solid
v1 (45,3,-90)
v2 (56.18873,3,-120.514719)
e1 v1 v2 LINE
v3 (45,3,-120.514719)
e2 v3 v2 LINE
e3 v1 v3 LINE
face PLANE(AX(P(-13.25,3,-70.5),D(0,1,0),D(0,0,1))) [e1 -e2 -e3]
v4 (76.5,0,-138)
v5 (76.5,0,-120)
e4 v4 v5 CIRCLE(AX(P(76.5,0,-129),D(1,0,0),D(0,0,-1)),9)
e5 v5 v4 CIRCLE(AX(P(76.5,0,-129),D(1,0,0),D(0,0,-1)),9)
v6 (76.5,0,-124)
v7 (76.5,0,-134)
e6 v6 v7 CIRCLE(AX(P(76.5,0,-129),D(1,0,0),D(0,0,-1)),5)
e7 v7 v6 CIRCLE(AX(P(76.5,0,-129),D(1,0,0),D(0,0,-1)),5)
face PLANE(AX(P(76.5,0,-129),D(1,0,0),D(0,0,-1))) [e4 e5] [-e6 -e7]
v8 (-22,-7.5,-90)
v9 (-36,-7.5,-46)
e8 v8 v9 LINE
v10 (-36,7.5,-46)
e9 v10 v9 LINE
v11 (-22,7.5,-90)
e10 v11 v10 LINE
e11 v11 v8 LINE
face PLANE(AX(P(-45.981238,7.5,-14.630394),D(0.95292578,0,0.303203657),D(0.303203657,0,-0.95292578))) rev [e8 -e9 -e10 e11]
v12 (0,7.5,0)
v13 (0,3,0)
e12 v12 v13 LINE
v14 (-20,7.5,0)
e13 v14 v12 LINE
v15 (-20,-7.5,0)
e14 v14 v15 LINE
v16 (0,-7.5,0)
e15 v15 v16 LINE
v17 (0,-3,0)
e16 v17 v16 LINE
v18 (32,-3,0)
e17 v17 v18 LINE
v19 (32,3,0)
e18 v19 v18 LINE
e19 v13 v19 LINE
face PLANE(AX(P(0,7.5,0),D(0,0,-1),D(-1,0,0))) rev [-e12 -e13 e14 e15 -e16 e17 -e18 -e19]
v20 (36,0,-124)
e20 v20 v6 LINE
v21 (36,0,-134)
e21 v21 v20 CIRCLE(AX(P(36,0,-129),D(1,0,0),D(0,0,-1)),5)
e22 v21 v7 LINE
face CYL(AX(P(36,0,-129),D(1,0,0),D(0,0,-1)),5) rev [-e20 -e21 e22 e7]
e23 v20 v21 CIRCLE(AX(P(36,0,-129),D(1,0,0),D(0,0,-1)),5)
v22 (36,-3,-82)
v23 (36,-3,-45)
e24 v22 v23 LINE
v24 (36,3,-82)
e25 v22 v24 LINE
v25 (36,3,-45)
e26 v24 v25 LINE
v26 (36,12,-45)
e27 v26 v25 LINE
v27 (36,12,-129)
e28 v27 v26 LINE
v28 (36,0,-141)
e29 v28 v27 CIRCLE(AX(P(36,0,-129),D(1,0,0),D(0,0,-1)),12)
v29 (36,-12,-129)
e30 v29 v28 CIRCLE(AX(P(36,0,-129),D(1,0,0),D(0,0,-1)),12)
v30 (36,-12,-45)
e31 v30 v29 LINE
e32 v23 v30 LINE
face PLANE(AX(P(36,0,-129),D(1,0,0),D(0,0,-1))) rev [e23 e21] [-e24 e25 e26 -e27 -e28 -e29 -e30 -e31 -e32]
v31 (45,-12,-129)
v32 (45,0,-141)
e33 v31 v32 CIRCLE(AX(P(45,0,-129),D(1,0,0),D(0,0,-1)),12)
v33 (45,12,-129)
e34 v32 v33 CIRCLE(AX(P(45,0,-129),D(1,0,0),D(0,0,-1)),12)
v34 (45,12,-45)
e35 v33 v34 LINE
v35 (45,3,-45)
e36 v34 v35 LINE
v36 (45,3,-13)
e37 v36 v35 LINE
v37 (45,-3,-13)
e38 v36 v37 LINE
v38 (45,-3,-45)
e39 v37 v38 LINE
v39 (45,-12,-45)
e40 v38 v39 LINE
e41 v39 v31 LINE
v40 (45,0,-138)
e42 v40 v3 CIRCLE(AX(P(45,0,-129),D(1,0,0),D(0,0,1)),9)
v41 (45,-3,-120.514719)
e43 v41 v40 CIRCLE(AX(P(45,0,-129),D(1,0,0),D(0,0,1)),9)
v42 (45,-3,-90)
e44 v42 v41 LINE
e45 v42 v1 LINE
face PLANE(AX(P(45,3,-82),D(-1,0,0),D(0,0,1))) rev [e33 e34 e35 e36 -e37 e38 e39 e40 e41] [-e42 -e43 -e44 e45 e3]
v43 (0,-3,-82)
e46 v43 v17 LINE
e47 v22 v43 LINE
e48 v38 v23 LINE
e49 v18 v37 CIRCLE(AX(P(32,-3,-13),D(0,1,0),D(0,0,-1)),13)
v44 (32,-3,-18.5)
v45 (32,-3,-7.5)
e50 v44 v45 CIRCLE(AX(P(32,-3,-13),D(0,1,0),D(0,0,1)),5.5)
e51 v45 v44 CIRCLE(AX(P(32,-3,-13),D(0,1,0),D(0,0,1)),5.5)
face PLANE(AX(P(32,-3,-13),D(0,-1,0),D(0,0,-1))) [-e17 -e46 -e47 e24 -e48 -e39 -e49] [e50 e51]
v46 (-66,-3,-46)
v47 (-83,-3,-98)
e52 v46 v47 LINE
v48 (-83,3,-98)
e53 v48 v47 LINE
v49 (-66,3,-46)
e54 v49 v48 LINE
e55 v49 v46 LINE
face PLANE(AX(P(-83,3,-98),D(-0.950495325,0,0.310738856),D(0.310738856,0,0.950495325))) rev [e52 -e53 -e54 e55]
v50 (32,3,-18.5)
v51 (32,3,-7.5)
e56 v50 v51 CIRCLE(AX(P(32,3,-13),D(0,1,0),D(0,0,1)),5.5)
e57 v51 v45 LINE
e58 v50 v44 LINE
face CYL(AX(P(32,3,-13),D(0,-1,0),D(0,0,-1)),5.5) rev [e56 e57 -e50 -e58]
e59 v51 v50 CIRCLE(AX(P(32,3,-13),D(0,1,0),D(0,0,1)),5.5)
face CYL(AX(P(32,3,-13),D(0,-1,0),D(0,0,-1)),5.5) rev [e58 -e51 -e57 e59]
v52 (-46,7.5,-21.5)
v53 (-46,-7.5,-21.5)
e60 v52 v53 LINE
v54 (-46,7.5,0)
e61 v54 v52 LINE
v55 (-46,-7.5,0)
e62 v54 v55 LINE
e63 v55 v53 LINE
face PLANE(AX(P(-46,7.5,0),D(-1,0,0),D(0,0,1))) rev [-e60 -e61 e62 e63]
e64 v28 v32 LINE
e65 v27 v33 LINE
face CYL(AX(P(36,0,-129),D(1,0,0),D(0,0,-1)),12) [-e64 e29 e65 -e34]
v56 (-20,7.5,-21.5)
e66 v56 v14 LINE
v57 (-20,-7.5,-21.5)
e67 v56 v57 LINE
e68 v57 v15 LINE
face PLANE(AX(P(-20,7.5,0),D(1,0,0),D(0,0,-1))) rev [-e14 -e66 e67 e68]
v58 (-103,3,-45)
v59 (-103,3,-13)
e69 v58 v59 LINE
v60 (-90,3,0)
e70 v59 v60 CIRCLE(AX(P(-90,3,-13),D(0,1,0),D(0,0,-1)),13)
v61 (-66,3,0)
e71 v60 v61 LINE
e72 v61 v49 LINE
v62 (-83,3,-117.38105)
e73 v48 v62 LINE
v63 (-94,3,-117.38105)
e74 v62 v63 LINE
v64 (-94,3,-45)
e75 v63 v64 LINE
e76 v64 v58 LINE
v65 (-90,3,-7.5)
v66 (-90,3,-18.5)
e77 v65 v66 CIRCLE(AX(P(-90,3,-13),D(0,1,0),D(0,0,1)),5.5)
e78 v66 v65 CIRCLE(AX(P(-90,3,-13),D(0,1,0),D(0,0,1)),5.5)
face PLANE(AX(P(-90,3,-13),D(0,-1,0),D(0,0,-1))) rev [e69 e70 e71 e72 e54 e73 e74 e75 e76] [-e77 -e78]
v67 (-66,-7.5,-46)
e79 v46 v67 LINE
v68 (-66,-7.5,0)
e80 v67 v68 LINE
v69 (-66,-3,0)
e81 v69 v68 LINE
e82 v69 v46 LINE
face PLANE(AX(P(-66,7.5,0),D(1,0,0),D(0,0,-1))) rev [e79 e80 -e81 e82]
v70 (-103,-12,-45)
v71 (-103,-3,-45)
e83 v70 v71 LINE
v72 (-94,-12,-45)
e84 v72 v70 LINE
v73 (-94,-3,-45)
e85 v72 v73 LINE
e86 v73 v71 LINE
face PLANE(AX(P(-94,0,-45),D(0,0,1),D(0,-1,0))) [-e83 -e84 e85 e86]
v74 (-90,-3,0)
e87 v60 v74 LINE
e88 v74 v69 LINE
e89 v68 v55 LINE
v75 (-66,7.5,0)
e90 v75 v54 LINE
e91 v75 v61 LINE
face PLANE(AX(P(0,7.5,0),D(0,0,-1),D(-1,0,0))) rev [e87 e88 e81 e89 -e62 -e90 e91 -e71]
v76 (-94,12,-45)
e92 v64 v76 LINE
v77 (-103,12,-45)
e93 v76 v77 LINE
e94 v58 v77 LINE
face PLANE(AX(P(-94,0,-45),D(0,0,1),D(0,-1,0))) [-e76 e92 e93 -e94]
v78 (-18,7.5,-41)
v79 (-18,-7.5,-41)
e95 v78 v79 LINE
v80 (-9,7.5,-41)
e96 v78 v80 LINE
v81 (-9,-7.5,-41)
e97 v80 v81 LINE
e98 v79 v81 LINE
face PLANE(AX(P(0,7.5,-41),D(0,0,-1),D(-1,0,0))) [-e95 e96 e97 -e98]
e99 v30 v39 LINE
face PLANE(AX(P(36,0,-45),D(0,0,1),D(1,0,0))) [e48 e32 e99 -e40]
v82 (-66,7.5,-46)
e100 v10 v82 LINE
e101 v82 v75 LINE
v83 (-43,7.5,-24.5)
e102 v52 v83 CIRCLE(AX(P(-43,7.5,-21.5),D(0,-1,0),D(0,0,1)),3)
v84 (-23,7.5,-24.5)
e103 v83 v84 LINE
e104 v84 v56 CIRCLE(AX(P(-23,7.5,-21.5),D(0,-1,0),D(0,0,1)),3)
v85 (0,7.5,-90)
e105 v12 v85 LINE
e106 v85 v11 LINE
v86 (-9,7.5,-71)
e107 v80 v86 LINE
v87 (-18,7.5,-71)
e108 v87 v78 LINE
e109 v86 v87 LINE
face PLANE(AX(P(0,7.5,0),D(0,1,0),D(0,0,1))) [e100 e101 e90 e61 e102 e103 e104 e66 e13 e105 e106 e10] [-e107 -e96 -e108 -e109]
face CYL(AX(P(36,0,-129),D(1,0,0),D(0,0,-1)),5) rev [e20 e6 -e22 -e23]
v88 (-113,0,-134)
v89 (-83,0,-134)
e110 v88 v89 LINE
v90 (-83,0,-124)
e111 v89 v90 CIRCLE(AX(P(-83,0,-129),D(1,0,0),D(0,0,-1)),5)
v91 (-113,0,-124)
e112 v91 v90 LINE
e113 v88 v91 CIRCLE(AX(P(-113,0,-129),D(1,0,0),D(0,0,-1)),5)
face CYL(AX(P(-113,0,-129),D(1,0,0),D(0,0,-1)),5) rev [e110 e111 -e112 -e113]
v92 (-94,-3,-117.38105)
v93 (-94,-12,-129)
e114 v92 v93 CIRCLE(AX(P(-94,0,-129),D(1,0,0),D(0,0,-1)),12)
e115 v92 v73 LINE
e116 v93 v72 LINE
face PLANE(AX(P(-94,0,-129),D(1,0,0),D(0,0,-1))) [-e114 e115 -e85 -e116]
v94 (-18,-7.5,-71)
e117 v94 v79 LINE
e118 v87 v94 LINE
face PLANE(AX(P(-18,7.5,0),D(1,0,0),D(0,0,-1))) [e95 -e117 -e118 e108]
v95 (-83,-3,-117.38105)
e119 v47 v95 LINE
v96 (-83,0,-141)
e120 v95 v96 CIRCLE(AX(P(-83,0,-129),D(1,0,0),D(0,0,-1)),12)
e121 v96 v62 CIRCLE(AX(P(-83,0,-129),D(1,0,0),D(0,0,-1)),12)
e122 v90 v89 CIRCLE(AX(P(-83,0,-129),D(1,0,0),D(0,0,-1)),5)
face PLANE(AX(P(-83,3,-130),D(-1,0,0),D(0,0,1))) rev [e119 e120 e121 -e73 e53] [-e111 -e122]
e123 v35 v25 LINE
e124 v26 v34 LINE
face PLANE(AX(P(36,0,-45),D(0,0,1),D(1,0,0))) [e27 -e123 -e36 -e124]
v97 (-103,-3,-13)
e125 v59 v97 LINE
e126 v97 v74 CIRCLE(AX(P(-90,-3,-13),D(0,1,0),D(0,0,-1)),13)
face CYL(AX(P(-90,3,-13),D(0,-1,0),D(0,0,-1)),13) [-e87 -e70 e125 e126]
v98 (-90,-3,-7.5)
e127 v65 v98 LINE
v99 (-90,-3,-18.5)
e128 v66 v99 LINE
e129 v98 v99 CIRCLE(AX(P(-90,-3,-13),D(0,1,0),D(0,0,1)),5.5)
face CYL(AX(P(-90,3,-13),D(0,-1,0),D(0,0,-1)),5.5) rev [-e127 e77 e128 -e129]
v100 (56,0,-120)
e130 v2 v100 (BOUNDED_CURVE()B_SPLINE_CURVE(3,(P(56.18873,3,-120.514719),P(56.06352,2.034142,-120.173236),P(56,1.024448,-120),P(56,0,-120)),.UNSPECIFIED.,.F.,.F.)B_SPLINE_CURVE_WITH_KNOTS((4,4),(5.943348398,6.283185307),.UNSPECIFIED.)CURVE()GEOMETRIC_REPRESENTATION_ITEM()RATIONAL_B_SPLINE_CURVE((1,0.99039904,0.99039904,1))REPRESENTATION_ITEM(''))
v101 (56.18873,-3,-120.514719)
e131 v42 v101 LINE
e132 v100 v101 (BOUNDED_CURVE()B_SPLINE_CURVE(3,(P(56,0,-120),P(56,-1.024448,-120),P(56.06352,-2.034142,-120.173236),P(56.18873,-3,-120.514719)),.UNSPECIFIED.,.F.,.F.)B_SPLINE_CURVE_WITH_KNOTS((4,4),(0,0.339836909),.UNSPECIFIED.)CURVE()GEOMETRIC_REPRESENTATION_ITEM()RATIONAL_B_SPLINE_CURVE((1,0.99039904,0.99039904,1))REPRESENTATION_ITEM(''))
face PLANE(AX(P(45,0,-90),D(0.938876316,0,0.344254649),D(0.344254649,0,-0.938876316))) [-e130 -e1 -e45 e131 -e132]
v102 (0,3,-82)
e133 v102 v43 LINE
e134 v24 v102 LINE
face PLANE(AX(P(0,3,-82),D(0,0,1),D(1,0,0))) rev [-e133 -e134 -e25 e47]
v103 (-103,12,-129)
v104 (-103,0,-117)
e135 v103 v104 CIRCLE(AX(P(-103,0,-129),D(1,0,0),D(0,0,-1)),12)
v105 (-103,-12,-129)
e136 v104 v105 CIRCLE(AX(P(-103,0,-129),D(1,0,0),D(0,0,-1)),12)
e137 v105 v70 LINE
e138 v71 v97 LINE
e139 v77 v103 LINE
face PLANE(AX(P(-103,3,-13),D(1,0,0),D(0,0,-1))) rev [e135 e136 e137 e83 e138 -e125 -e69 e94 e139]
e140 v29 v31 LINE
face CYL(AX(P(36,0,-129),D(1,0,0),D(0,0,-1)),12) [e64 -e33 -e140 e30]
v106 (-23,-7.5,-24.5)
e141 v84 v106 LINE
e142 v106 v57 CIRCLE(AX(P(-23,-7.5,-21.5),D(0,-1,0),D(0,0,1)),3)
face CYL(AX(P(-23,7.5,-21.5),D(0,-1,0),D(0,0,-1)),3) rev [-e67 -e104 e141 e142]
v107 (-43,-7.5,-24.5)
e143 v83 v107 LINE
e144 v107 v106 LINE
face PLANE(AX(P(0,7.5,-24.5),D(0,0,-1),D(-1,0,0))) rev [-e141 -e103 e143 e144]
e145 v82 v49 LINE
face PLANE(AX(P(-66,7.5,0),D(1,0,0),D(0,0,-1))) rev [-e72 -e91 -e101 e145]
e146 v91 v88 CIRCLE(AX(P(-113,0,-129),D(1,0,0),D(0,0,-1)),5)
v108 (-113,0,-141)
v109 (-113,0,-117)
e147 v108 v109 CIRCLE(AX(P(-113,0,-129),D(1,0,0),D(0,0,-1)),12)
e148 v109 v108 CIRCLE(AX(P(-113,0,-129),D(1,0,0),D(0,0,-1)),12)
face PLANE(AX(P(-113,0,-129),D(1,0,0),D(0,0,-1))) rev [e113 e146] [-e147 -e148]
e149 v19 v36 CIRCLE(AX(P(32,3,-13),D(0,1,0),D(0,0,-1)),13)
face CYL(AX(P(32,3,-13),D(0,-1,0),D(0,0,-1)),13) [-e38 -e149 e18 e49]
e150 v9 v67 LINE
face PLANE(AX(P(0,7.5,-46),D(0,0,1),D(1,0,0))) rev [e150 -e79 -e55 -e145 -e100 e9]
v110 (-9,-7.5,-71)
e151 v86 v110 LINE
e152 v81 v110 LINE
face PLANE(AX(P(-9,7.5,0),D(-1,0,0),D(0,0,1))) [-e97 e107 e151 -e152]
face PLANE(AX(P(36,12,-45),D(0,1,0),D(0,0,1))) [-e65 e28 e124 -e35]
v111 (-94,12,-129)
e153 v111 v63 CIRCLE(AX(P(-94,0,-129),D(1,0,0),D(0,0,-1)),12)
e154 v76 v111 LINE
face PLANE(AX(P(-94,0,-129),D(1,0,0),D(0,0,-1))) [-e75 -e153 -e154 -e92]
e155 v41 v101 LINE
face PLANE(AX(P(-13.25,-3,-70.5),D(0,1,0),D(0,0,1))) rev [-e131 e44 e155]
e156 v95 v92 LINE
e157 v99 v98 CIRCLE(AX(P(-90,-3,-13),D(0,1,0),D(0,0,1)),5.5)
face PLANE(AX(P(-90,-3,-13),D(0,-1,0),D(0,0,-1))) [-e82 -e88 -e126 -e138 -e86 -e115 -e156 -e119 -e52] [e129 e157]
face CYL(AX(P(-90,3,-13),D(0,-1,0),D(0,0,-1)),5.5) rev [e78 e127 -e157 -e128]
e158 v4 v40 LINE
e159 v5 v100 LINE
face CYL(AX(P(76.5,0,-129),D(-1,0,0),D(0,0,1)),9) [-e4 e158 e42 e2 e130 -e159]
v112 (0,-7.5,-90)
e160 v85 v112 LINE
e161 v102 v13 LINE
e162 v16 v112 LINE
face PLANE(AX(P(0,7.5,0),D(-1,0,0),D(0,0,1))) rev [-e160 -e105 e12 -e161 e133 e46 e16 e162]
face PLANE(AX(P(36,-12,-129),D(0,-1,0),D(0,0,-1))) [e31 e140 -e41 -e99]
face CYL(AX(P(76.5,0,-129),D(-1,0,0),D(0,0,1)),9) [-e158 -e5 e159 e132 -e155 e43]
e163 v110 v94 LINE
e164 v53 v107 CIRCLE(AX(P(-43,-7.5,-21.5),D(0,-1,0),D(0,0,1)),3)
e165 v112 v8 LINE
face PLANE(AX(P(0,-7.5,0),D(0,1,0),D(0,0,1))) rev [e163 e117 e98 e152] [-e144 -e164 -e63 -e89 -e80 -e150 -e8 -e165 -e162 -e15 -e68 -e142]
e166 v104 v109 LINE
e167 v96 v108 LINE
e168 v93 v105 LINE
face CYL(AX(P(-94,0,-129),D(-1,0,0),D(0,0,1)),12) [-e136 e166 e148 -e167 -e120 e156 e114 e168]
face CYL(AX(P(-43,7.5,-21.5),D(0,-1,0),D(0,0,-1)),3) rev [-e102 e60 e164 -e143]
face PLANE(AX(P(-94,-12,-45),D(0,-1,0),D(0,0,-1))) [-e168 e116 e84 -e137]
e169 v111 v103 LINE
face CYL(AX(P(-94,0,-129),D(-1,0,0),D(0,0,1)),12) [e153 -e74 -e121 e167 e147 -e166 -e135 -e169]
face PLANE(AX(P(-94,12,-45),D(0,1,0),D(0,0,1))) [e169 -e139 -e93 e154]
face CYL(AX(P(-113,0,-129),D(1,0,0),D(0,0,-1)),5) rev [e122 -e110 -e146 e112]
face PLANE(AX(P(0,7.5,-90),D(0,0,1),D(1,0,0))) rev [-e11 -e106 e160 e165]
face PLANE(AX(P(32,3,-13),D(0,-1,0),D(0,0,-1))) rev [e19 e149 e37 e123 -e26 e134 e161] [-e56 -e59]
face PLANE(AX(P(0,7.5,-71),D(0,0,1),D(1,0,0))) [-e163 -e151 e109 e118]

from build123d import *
from build123d.topology import SkipClean

# Parameters (mm, degrees)
BASE_PLATE_SKETCH_W              = 9
BASE_PLATE_SKETCH_H              = 30
BASE_PLATE_DEPTH                 = 7.5
RAISED_PAD_SKETCH_R              = 5.5
RAISED_PAD_DEPTH                 = 3
ARM_BLOCK_SKETCH_R               = 5
ARM_BLOCK_DEPTH                  = 9
FIRST_START                      = 31.5
FIRST_ARM_PIVOT_BOSS_SKETCH_R    = 9
FIRST_ARM_PIVOT_BOSS_SKETCH_R_2  = 5
FIRST_ARM_PIVOT_BOSS_DEPTH       = 31.5
ARM_RIB_REACH                    = 177.026
ARM_RIB_SKETCH_WALL_W            = 384.00451541
ARM_RIB_SKETCH_WALL_H            = 6
SECOND_START                     = -9
SECOND_ARM_DEPTH                 = 9
SECOND_ARM_PIVOT_BOSS_DEPTH      = 11
SECOND_ARM_PIVOT_BOSS_DEPTH_BACK = 19
SECOND_ARM_PIVOT_BOSS_SKETCH_R   = 12
PIVOT_BORE_SKETCH_R              = 5
PIVOT_BORE_DEPTH                 = 214.225819262


with BuildPart() as part:
    # Base Plate Sketch → Base Plate (new, symmetric)
    with BuildSketch(Plane(origin=(0, 0, 0), x_dir=(1, 0, 0), z_dir=(0, 1, 0))):
        with BuildLine():
            Line((-43, 24.5), (-23, 24.5))
            ThreePointArc((-23, 24.5), (-20.878679656, 23.621320344), (-20, 21.5))
            Line((-20, 21.5), (-20, 0))
            Line((-20, 0), (0, 0))
            Line((0, 0), (0, 90))
            Line((0, 90), (-22, 90))
            Line((-22, 90), (-36, 46))
            Line((-36, 46), (-66, 46))
            Line((-66, 46), (-66, 0))
            Line((-66, 0), (-46, 0))
            Line((-46, 0), (-46, 21.5))
            ThreePointArc((-46, 21.5), (-45.121320344, 23.621320344), (-43, 24.5))
        make_face()
        with Locations((-13.5, 56)):
            Rectangle(BASE_PLATE_SKETCH_W, BASE_PLATE_SKETCH_H, mode=Mode.SUBTRACT)
    extrude(amount=BASE_PLATE_DEPTH, both=True)

    # Raised Pad Sketch → Raised Pad (add, symmetric)
    # profile 1 of 2: a face of its own
    with BuildSketch(Plane(origin=(0, 0, 0), x_dir=(1, 0, 0), z_dir=(0, 1, 0))):
        with BuildLine():
            Line((0, 82), (45, 82))
            Line((45, 82), (45, 13))
            ThreePointArc((45, 13), (41.192388155, 3.807611845), (32, 0))
            Line((32, 0), (0, 0))
            Line((0, 0), (0, 82))
        make_face()
        with Locations(Location((32, 13, 0), (0, 0, 270))):
            Circle(RAISED_PAD_SKETCH_R, mode=Mode.SUBTRACT)
    # profile 2 of 2: a face of its own
    with BuildSketch(Plane(origin=(0, 0, 0), x_dir=(1, 0, 0), z_dir=(0, 1, 0))):
        with BuildLine():
            Line((-66, 0), (-90, 0))
            ThreePointArc((-90, 0), (-99.192388155, 3.807611845), (-103, 13))
            Line((-103, 13), (-103, 130))
            Line((-103, 130), (-83, 130))
            Line((-83, 130), (-83, 98))
            Line((-83, 98), (-66, 46))
            Line((-66, 46), (-66, 0))
        make_face()
        with Locations(Location((-90, 13, 0), (0, 0, 270))):
            Circle(RAISED_PAD_SKETCH_R, mode=Mode.SUBTRACT)
    extrude(amount=RAISED_PAD_DEPTH, both=True)

    # Arm Block Sketch → Arm Block (add)
    with BuildSketch(Plane(origin=(45, 0, 0), x_dir=(0, 0, -1), z_dir=(1, 0, 0))):
        with BuildLine():
            Line((45, 0), (45, 12))
            Line((45, 12), (129, 12))
            ThreePointArc((129, 12), (141, 0), (129, -12))
            Line((129, -12), (45, -12))
            Line((45, -12), (45, 0))
        make_face()
        with Locations((129, 0)):
            Circle(ARM_BLOCK_SKETCH_R, mode=Mode.SUBTRACT)
    extrude(amount=-ARM_BLOCK_DEPTH)

    # First Arm Pivot Boss Sketch → First Arm Pivot Boss (add)
    with BuildSketch(Plane(origin=(45, 0, 0), x_dir=(0, 0, -1), z_dir=(1, 0, 0)).offset(FIRST_START)):
        with Locations(Location((129, 0, 0), (0, 0, 180))):
            Circle(FIRST_ARM_PIVOT_BOSS_SKETCH_R)
        with Locations((129, 0)):
            Circle(FIRST_ARM_PIVOT_BOSS_SKETCH_R_2, mode=Mode.SUBTRACT)
    extrude(amount=-FIRST_ARM_PIVOT_BOSS_DEPTH)

    # Arm Rib Sketch wall → Arm Rib (add, up to next)
    with BuildSketch(Plane(origin=(50.5, 0, -105), x_dir=(0.344254649158, 0, -0.938876315887), z_dir=(-0.938876315887, 0, -0.344254649158)), mode=Mode.PRIVATE) as arm_rib_sk1:
        Rectangle(ARM_RIB_SKETCH_WALL_W, ARM_RIB_SKETCH_WALL_H)
    arm_rib_tool1 = extrude(arm_rib_sk1.sketch, amount=ARM_RIB_REACH, mode=Mode.PRIVATE) - part.part
    add(arm_rib_tool1.solids().sort_by_distance((50.5, 0, -105))[0])

    # Second Arm Sketch → Second Arm (add)
    with BuildSketch(Plane.ZY.offset(103).offset(SECOND_START)):
        with BuildLine():
            Line((-45, 0), (-45, 12))
            Line((-45, 12), (-129, 12))
            ThreePointArc((-129, 12), (-141, 0), (-129, -12))
            Line((-129, -12), (-45, -12))
            Line((-45, -12), (-45, 0))
        make_face()
    extrude(amount=SECOND_ARM_DEPTH)

    # Second Arm Pivot Boss Sketch → Second Arm Pivot Boss (add, two sides: drawn at the far end of the back side and taken through both)
    with SkipClean():  # the faces are left unmerged after this step: merging them gives an invalid solid
        with BuildSketch(Plane(origin=(-94, 0, 0), x_dir=(0, 0, -1), z_dir=(1, 0, 0)).offset(-SECOND_ARM_PIVOT_BOSS_DEPTH_BACK)):
            with Locations(Location((129, 0, 0), (0, 0, 194.477512186))):
                Circle(SECOND_ARM_PIVOT_BOSS_SKETCH_R)
        extrude(amount=SECOND_ARM_PIVOT_BOSS_DEPTH + SECOND_ARM_PIVOT_BOSS_DEPTH_BACK)

    # Pivot Bore Sketch → Pivot Bore (cut, through all)
    with SkipClean():  # the faces are left unmerged after this step: merging them gives an invalid solid
        with BuildSketch(Plane(origin=(-83, 0, 0), x_dir=(0, 0, -1), z_dir=(1, 0, 0))):
            with Locations((129, 0)):
                Circle(PIVOT_BORE_SKETCH_R)
        extrude(amount=-PIVOT_BORE_DEPTH, mode=Mode.SUBTRACT)


solid = part.part
